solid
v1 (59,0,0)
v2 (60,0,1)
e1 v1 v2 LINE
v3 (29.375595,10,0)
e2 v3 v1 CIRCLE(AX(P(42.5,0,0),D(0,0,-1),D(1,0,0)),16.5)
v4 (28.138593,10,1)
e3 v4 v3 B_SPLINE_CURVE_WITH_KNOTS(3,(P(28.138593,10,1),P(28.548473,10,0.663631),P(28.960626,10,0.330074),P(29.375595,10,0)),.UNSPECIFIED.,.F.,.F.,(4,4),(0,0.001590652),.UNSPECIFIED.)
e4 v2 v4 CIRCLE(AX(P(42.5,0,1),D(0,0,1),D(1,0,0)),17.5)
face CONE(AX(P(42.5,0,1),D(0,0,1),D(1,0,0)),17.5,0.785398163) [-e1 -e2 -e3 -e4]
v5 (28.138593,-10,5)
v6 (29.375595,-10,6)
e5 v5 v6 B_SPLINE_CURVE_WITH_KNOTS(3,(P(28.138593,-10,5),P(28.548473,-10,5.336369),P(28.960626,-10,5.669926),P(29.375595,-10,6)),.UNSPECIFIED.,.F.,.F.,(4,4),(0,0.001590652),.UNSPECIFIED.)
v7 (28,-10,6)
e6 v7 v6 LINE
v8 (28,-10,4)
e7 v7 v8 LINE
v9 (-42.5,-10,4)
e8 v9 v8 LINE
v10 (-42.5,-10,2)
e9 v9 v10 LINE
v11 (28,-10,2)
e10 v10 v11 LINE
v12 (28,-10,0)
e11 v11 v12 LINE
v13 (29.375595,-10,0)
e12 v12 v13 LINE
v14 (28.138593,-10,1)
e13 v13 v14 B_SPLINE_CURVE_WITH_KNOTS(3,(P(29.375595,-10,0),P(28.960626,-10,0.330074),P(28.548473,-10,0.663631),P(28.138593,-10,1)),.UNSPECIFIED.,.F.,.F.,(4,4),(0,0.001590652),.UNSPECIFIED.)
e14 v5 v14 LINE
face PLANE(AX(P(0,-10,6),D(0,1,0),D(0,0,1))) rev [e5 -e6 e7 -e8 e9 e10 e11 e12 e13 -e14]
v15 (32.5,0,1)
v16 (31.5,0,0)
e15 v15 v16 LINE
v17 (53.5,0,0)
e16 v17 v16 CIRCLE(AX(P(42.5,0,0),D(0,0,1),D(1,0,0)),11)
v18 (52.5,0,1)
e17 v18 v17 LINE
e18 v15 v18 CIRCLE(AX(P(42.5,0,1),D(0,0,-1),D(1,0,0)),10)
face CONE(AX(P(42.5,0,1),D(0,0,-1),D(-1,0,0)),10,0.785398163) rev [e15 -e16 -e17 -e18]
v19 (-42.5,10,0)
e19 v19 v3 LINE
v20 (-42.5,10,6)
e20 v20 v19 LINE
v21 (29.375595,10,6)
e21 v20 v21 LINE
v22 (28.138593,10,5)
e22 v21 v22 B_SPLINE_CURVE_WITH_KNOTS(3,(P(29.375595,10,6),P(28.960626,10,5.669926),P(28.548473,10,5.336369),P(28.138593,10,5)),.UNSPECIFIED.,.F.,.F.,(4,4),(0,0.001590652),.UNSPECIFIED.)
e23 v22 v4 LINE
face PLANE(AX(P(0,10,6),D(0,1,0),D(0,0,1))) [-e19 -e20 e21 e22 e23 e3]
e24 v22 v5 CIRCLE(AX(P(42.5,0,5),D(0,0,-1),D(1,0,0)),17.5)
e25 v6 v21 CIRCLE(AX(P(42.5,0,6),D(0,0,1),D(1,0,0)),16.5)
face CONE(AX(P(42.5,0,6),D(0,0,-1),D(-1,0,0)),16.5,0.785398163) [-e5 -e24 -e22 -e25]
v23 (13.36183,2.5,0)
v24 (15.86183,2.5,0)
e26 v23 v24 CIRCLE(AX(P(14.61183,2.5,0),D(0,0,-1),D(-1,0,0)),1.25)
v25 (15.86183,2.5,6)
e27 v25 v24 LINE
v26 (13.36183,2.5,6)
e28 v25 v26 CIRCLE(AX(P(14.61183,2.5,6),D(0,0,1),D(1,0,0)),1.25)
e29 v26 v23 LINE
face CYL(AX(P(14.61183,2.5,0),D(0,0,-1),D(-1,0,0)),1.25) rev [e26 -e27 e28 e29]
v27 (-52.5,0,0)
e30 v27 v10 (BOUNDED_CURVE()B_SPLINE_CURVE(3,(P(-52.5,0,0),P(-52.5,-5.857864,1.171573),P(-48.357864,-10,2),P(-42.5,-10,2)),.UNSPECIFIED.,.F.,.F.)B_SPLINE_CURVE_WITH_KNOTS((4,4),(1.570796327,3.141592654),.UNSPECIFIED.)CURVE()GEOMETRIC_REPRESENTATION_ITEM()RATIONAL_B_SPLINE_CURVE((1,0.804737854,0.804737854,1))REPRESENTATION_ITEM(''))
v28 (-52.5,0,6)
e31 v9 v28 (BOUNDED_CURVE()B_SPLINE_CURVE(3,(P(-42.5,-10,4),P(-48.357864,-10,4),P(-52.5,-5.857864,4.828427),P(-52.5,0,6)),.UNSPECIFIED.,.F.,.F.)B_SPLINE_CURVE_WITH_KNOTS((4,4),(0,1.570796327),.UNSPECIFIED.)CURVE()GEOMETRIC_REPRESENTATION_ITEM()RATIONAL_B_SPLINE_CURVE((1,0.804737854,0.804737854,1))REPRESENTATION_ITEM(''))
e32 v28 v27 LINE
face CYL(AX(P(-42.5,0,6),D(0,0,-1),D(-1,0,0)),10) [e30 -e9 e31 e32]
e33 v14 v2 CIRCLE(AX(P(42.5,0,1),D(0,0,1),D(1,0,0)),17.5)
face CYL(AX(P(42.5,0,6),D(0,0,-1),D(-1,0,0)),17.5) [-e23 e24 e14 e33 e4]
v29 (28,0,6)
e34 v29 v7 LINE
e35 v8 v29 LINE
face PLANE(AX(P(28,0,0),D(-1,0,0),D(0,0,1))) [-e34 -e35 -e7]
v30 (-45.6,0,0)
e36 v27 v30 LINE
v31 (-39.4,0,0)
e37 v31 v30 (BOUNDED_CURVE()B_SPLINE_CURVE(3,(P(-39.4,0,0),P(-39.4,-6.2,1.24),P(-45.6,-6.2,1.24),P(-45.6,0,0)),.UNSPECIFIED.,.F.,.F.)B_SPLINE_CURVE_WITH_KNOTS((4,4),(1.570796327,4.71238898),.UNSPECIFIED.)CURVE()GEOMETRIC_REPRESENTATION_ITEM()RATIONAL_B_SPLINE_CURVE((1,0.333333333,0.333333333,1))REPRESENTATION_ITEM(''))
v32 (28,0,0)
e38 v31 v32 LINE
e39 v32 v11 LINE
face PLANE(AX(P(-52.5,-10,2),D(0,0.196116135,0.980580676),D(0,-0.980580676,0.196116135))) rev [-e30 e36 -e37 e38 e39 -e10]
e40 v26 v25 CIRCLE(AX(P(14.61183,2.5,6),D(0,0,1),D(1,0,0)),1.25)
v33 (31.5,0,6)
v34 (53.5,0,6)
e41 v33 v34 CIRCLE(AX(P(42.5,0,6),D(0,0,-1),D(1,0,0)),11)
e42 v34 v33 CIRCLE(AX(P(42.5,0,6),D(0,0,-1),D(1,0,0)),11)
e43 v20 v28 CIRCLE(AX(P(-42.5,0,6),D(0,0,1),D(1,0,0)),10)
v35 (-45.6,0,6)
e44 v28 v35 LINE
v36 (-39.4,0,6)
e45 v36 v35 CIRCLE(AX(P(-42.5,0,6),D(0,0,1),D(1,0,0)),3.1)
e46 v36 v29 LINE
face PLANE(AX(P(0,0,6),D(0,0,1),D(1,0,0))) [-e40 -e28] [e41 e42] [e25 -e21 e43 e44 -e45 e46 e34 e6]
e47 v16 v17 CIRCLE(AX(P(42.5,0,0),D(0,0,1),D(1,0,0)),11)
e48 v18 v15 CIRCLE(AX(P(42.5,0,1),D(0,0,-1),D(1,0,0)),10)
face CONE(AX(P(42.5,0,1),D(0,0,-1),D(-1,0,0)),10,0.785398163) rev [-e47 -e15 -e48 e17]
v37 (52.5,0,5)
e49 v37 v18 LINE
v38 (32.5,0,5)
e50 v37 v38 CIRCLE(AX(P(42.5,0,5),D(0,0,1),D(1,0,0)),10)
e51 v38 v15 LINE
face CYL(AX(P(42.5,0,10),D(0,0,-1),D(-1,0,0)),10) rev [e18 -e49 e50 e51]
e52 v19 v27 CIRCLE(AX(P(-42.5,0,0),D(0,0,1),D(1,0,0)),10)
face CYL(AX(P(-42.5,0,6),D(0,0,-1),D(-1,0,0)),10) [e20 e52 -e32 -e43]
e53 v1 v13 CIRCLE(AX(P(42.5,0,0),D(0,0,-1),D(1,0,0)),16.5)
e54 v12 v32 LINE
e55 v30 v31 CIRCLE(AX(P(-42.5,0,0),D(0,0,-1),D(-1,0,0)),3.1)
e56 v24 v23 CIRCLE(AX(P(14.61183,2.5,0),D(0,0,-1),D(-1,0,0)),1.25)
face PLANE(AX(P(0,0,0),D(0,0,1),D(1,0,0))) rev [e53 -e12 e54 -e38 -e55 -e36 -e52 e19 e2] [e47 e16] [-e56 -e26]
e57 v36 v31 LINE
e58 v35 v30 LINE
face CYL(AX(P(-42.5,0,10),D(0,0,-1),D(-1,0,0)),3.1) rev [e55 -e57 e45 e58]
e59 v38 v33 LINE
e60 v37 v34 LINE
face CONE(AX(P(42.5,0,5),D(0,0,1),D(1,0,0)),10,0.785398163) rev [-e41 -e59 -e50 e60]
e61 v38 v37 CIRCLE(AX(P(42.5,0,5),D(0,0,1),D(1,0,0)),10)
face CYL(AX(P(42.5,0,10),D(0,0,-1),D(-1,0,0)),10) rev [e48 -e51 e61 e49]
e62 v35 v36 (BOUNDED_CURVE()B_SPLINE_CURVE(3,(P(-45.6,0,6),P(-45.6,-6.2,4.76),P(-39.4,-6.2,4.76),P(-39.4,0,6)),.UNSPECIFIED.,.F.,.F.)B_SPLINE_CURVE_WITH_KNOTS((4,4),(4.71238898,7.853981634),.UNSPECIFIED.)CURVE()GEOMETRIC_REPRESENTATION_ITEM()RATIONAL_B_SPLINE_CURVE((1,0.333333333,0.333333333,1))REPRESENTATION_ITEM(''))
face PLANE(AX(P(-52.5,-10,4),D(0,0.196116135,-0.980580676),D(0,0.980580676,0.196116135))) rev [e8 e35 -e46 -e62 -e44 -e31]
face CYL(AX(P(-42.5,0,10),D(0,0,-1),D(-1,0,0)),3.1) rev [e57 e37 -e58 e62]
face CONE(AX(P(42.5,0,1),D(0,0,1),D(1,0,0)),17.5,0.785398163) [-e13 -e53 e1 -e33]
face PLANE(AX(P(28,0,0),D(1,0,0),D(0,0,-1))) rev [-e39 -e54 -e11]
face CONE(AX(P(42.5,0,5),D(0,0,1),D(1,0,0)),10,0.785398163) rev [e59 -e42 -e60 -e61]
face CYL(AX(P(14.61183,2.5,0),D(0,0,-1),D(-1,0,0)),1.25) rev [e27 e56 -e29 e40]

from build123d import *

# Parameters (mm, degrees)
SKETCH_6_R             = 17.5
EXTRUDE_3_DEPTH        = 6
SKETCH_7_R             = 10
CUT_EXTRUDE_1_DEPTH    = 10
SKETCH_8_R             = 3.1
CUT_EXTRUDE_2_DEPTH    = 10
CUT_EXTRUDE_3_DEPTH    = 83.598426135
CHAMFER_1_SIZE         = 1
HOLE_WIZARD_M3_1_D     = 2.5
HOLE_WIZARD_M3_1_DEPTH = 8.5
HOLE_WIZARD_M3_1_TIP   = 0.751075774


with BuildPart() as part:
    # 草图6 → 凸台-拉伸3 (new body)
    with BuildSketch(Plane.XY):
        with Locations((42.5, 0)):
            Circle(SKETCH_6_R)
        with BuildLine():
            Line((-42.5, 10), (42.5, 10))
            ThreePointArc((42.5, 10), (52.5, 0), (42.5, -10))
            Line((42.5, -10), (-42.5, -10))
            ThreePointArc((-42.5, -10), (-52.5, 0), (-42.5, 10))
        make_face()
    extrude(amount=EXTRUDE_3_DEPTH)

    # 草图7 → 切除-拉伸1 (cut)
    with BuildSketch(Plane(origin=(0, 0, 0), x_dir=(-1, 0, 0), z_dir=(0, 0, -1))):
        with Locations((-42.5, 0)):
            Circle(SKETCH_7_R)
    extrude(amount=-CUT_EXTRUDE_1_DEPTH, mode=Mode.SUBTRACT)

    # 草图8 → 切除-拉伸2 (cut)
    with BuildSketch(Plane(origin=(0, 0, 0), x_dir=(-1, 0, 0), z_dir=(0, 0, -1))):
        with Locations((42.5, 0)):
            Circle(SKETCH_8_R)
    extrude(amount=-CUT_EXTRUDE_2_DEPTH, mode=Mode.SUBTRACT)

    # 草图9 → 切除-拉伸3 (cut, through all)
    with BuildSketch(Plane(origin=(28, 0, 0), x_dir=(0, 0, -1), z_dir=(1, 0, 0))):
        Polygon((-4, -10), (-6, 0), (-6, -10), align=None)
        Polygon((-2, -10), (0, 0), (0, -10), align=None)
    extrude(amount=-CUT_EXTRUDE_3_DEPTH, mode=Mode.SUBTRACT)

    # 倒角1
    chamfer_1_edges = [part.edges().sort_by_distance(p)[0] for p in [
        (60, 0, 6),
        (52.5, 0, 6),
        (52.5, 0, 0),
        (60, 0, 0),
    ]]
    chamfer(chamfer_1_edges, length=CHAMFER_1_SIZE)

    # M3 螺纹孔1
    with Locations(Plane(origin=(0, 0, 0), x_dir=(-1, 0, 0), z_dir=(0, 0, -1))):
        with Locations((-14.611830465, 2.5)):
            Hole(HOLE_WIZARD_M3_1_D / 2, depth=HOLE_WIZARD_M3_1_DEPTH)
            with Locations((0, 0, -(HOLE_WIZARD_M3_1_DEPTH + HOLE_WIZARD_M3_1_TIP / 2))):  # 118° drill point
                Cone(0, HOLE_WIZARD_M3_1_D / 2, HOLE_WIZARD_M3_1_TIP, mode=Mode.SUBTRACT)


solid = part.part
